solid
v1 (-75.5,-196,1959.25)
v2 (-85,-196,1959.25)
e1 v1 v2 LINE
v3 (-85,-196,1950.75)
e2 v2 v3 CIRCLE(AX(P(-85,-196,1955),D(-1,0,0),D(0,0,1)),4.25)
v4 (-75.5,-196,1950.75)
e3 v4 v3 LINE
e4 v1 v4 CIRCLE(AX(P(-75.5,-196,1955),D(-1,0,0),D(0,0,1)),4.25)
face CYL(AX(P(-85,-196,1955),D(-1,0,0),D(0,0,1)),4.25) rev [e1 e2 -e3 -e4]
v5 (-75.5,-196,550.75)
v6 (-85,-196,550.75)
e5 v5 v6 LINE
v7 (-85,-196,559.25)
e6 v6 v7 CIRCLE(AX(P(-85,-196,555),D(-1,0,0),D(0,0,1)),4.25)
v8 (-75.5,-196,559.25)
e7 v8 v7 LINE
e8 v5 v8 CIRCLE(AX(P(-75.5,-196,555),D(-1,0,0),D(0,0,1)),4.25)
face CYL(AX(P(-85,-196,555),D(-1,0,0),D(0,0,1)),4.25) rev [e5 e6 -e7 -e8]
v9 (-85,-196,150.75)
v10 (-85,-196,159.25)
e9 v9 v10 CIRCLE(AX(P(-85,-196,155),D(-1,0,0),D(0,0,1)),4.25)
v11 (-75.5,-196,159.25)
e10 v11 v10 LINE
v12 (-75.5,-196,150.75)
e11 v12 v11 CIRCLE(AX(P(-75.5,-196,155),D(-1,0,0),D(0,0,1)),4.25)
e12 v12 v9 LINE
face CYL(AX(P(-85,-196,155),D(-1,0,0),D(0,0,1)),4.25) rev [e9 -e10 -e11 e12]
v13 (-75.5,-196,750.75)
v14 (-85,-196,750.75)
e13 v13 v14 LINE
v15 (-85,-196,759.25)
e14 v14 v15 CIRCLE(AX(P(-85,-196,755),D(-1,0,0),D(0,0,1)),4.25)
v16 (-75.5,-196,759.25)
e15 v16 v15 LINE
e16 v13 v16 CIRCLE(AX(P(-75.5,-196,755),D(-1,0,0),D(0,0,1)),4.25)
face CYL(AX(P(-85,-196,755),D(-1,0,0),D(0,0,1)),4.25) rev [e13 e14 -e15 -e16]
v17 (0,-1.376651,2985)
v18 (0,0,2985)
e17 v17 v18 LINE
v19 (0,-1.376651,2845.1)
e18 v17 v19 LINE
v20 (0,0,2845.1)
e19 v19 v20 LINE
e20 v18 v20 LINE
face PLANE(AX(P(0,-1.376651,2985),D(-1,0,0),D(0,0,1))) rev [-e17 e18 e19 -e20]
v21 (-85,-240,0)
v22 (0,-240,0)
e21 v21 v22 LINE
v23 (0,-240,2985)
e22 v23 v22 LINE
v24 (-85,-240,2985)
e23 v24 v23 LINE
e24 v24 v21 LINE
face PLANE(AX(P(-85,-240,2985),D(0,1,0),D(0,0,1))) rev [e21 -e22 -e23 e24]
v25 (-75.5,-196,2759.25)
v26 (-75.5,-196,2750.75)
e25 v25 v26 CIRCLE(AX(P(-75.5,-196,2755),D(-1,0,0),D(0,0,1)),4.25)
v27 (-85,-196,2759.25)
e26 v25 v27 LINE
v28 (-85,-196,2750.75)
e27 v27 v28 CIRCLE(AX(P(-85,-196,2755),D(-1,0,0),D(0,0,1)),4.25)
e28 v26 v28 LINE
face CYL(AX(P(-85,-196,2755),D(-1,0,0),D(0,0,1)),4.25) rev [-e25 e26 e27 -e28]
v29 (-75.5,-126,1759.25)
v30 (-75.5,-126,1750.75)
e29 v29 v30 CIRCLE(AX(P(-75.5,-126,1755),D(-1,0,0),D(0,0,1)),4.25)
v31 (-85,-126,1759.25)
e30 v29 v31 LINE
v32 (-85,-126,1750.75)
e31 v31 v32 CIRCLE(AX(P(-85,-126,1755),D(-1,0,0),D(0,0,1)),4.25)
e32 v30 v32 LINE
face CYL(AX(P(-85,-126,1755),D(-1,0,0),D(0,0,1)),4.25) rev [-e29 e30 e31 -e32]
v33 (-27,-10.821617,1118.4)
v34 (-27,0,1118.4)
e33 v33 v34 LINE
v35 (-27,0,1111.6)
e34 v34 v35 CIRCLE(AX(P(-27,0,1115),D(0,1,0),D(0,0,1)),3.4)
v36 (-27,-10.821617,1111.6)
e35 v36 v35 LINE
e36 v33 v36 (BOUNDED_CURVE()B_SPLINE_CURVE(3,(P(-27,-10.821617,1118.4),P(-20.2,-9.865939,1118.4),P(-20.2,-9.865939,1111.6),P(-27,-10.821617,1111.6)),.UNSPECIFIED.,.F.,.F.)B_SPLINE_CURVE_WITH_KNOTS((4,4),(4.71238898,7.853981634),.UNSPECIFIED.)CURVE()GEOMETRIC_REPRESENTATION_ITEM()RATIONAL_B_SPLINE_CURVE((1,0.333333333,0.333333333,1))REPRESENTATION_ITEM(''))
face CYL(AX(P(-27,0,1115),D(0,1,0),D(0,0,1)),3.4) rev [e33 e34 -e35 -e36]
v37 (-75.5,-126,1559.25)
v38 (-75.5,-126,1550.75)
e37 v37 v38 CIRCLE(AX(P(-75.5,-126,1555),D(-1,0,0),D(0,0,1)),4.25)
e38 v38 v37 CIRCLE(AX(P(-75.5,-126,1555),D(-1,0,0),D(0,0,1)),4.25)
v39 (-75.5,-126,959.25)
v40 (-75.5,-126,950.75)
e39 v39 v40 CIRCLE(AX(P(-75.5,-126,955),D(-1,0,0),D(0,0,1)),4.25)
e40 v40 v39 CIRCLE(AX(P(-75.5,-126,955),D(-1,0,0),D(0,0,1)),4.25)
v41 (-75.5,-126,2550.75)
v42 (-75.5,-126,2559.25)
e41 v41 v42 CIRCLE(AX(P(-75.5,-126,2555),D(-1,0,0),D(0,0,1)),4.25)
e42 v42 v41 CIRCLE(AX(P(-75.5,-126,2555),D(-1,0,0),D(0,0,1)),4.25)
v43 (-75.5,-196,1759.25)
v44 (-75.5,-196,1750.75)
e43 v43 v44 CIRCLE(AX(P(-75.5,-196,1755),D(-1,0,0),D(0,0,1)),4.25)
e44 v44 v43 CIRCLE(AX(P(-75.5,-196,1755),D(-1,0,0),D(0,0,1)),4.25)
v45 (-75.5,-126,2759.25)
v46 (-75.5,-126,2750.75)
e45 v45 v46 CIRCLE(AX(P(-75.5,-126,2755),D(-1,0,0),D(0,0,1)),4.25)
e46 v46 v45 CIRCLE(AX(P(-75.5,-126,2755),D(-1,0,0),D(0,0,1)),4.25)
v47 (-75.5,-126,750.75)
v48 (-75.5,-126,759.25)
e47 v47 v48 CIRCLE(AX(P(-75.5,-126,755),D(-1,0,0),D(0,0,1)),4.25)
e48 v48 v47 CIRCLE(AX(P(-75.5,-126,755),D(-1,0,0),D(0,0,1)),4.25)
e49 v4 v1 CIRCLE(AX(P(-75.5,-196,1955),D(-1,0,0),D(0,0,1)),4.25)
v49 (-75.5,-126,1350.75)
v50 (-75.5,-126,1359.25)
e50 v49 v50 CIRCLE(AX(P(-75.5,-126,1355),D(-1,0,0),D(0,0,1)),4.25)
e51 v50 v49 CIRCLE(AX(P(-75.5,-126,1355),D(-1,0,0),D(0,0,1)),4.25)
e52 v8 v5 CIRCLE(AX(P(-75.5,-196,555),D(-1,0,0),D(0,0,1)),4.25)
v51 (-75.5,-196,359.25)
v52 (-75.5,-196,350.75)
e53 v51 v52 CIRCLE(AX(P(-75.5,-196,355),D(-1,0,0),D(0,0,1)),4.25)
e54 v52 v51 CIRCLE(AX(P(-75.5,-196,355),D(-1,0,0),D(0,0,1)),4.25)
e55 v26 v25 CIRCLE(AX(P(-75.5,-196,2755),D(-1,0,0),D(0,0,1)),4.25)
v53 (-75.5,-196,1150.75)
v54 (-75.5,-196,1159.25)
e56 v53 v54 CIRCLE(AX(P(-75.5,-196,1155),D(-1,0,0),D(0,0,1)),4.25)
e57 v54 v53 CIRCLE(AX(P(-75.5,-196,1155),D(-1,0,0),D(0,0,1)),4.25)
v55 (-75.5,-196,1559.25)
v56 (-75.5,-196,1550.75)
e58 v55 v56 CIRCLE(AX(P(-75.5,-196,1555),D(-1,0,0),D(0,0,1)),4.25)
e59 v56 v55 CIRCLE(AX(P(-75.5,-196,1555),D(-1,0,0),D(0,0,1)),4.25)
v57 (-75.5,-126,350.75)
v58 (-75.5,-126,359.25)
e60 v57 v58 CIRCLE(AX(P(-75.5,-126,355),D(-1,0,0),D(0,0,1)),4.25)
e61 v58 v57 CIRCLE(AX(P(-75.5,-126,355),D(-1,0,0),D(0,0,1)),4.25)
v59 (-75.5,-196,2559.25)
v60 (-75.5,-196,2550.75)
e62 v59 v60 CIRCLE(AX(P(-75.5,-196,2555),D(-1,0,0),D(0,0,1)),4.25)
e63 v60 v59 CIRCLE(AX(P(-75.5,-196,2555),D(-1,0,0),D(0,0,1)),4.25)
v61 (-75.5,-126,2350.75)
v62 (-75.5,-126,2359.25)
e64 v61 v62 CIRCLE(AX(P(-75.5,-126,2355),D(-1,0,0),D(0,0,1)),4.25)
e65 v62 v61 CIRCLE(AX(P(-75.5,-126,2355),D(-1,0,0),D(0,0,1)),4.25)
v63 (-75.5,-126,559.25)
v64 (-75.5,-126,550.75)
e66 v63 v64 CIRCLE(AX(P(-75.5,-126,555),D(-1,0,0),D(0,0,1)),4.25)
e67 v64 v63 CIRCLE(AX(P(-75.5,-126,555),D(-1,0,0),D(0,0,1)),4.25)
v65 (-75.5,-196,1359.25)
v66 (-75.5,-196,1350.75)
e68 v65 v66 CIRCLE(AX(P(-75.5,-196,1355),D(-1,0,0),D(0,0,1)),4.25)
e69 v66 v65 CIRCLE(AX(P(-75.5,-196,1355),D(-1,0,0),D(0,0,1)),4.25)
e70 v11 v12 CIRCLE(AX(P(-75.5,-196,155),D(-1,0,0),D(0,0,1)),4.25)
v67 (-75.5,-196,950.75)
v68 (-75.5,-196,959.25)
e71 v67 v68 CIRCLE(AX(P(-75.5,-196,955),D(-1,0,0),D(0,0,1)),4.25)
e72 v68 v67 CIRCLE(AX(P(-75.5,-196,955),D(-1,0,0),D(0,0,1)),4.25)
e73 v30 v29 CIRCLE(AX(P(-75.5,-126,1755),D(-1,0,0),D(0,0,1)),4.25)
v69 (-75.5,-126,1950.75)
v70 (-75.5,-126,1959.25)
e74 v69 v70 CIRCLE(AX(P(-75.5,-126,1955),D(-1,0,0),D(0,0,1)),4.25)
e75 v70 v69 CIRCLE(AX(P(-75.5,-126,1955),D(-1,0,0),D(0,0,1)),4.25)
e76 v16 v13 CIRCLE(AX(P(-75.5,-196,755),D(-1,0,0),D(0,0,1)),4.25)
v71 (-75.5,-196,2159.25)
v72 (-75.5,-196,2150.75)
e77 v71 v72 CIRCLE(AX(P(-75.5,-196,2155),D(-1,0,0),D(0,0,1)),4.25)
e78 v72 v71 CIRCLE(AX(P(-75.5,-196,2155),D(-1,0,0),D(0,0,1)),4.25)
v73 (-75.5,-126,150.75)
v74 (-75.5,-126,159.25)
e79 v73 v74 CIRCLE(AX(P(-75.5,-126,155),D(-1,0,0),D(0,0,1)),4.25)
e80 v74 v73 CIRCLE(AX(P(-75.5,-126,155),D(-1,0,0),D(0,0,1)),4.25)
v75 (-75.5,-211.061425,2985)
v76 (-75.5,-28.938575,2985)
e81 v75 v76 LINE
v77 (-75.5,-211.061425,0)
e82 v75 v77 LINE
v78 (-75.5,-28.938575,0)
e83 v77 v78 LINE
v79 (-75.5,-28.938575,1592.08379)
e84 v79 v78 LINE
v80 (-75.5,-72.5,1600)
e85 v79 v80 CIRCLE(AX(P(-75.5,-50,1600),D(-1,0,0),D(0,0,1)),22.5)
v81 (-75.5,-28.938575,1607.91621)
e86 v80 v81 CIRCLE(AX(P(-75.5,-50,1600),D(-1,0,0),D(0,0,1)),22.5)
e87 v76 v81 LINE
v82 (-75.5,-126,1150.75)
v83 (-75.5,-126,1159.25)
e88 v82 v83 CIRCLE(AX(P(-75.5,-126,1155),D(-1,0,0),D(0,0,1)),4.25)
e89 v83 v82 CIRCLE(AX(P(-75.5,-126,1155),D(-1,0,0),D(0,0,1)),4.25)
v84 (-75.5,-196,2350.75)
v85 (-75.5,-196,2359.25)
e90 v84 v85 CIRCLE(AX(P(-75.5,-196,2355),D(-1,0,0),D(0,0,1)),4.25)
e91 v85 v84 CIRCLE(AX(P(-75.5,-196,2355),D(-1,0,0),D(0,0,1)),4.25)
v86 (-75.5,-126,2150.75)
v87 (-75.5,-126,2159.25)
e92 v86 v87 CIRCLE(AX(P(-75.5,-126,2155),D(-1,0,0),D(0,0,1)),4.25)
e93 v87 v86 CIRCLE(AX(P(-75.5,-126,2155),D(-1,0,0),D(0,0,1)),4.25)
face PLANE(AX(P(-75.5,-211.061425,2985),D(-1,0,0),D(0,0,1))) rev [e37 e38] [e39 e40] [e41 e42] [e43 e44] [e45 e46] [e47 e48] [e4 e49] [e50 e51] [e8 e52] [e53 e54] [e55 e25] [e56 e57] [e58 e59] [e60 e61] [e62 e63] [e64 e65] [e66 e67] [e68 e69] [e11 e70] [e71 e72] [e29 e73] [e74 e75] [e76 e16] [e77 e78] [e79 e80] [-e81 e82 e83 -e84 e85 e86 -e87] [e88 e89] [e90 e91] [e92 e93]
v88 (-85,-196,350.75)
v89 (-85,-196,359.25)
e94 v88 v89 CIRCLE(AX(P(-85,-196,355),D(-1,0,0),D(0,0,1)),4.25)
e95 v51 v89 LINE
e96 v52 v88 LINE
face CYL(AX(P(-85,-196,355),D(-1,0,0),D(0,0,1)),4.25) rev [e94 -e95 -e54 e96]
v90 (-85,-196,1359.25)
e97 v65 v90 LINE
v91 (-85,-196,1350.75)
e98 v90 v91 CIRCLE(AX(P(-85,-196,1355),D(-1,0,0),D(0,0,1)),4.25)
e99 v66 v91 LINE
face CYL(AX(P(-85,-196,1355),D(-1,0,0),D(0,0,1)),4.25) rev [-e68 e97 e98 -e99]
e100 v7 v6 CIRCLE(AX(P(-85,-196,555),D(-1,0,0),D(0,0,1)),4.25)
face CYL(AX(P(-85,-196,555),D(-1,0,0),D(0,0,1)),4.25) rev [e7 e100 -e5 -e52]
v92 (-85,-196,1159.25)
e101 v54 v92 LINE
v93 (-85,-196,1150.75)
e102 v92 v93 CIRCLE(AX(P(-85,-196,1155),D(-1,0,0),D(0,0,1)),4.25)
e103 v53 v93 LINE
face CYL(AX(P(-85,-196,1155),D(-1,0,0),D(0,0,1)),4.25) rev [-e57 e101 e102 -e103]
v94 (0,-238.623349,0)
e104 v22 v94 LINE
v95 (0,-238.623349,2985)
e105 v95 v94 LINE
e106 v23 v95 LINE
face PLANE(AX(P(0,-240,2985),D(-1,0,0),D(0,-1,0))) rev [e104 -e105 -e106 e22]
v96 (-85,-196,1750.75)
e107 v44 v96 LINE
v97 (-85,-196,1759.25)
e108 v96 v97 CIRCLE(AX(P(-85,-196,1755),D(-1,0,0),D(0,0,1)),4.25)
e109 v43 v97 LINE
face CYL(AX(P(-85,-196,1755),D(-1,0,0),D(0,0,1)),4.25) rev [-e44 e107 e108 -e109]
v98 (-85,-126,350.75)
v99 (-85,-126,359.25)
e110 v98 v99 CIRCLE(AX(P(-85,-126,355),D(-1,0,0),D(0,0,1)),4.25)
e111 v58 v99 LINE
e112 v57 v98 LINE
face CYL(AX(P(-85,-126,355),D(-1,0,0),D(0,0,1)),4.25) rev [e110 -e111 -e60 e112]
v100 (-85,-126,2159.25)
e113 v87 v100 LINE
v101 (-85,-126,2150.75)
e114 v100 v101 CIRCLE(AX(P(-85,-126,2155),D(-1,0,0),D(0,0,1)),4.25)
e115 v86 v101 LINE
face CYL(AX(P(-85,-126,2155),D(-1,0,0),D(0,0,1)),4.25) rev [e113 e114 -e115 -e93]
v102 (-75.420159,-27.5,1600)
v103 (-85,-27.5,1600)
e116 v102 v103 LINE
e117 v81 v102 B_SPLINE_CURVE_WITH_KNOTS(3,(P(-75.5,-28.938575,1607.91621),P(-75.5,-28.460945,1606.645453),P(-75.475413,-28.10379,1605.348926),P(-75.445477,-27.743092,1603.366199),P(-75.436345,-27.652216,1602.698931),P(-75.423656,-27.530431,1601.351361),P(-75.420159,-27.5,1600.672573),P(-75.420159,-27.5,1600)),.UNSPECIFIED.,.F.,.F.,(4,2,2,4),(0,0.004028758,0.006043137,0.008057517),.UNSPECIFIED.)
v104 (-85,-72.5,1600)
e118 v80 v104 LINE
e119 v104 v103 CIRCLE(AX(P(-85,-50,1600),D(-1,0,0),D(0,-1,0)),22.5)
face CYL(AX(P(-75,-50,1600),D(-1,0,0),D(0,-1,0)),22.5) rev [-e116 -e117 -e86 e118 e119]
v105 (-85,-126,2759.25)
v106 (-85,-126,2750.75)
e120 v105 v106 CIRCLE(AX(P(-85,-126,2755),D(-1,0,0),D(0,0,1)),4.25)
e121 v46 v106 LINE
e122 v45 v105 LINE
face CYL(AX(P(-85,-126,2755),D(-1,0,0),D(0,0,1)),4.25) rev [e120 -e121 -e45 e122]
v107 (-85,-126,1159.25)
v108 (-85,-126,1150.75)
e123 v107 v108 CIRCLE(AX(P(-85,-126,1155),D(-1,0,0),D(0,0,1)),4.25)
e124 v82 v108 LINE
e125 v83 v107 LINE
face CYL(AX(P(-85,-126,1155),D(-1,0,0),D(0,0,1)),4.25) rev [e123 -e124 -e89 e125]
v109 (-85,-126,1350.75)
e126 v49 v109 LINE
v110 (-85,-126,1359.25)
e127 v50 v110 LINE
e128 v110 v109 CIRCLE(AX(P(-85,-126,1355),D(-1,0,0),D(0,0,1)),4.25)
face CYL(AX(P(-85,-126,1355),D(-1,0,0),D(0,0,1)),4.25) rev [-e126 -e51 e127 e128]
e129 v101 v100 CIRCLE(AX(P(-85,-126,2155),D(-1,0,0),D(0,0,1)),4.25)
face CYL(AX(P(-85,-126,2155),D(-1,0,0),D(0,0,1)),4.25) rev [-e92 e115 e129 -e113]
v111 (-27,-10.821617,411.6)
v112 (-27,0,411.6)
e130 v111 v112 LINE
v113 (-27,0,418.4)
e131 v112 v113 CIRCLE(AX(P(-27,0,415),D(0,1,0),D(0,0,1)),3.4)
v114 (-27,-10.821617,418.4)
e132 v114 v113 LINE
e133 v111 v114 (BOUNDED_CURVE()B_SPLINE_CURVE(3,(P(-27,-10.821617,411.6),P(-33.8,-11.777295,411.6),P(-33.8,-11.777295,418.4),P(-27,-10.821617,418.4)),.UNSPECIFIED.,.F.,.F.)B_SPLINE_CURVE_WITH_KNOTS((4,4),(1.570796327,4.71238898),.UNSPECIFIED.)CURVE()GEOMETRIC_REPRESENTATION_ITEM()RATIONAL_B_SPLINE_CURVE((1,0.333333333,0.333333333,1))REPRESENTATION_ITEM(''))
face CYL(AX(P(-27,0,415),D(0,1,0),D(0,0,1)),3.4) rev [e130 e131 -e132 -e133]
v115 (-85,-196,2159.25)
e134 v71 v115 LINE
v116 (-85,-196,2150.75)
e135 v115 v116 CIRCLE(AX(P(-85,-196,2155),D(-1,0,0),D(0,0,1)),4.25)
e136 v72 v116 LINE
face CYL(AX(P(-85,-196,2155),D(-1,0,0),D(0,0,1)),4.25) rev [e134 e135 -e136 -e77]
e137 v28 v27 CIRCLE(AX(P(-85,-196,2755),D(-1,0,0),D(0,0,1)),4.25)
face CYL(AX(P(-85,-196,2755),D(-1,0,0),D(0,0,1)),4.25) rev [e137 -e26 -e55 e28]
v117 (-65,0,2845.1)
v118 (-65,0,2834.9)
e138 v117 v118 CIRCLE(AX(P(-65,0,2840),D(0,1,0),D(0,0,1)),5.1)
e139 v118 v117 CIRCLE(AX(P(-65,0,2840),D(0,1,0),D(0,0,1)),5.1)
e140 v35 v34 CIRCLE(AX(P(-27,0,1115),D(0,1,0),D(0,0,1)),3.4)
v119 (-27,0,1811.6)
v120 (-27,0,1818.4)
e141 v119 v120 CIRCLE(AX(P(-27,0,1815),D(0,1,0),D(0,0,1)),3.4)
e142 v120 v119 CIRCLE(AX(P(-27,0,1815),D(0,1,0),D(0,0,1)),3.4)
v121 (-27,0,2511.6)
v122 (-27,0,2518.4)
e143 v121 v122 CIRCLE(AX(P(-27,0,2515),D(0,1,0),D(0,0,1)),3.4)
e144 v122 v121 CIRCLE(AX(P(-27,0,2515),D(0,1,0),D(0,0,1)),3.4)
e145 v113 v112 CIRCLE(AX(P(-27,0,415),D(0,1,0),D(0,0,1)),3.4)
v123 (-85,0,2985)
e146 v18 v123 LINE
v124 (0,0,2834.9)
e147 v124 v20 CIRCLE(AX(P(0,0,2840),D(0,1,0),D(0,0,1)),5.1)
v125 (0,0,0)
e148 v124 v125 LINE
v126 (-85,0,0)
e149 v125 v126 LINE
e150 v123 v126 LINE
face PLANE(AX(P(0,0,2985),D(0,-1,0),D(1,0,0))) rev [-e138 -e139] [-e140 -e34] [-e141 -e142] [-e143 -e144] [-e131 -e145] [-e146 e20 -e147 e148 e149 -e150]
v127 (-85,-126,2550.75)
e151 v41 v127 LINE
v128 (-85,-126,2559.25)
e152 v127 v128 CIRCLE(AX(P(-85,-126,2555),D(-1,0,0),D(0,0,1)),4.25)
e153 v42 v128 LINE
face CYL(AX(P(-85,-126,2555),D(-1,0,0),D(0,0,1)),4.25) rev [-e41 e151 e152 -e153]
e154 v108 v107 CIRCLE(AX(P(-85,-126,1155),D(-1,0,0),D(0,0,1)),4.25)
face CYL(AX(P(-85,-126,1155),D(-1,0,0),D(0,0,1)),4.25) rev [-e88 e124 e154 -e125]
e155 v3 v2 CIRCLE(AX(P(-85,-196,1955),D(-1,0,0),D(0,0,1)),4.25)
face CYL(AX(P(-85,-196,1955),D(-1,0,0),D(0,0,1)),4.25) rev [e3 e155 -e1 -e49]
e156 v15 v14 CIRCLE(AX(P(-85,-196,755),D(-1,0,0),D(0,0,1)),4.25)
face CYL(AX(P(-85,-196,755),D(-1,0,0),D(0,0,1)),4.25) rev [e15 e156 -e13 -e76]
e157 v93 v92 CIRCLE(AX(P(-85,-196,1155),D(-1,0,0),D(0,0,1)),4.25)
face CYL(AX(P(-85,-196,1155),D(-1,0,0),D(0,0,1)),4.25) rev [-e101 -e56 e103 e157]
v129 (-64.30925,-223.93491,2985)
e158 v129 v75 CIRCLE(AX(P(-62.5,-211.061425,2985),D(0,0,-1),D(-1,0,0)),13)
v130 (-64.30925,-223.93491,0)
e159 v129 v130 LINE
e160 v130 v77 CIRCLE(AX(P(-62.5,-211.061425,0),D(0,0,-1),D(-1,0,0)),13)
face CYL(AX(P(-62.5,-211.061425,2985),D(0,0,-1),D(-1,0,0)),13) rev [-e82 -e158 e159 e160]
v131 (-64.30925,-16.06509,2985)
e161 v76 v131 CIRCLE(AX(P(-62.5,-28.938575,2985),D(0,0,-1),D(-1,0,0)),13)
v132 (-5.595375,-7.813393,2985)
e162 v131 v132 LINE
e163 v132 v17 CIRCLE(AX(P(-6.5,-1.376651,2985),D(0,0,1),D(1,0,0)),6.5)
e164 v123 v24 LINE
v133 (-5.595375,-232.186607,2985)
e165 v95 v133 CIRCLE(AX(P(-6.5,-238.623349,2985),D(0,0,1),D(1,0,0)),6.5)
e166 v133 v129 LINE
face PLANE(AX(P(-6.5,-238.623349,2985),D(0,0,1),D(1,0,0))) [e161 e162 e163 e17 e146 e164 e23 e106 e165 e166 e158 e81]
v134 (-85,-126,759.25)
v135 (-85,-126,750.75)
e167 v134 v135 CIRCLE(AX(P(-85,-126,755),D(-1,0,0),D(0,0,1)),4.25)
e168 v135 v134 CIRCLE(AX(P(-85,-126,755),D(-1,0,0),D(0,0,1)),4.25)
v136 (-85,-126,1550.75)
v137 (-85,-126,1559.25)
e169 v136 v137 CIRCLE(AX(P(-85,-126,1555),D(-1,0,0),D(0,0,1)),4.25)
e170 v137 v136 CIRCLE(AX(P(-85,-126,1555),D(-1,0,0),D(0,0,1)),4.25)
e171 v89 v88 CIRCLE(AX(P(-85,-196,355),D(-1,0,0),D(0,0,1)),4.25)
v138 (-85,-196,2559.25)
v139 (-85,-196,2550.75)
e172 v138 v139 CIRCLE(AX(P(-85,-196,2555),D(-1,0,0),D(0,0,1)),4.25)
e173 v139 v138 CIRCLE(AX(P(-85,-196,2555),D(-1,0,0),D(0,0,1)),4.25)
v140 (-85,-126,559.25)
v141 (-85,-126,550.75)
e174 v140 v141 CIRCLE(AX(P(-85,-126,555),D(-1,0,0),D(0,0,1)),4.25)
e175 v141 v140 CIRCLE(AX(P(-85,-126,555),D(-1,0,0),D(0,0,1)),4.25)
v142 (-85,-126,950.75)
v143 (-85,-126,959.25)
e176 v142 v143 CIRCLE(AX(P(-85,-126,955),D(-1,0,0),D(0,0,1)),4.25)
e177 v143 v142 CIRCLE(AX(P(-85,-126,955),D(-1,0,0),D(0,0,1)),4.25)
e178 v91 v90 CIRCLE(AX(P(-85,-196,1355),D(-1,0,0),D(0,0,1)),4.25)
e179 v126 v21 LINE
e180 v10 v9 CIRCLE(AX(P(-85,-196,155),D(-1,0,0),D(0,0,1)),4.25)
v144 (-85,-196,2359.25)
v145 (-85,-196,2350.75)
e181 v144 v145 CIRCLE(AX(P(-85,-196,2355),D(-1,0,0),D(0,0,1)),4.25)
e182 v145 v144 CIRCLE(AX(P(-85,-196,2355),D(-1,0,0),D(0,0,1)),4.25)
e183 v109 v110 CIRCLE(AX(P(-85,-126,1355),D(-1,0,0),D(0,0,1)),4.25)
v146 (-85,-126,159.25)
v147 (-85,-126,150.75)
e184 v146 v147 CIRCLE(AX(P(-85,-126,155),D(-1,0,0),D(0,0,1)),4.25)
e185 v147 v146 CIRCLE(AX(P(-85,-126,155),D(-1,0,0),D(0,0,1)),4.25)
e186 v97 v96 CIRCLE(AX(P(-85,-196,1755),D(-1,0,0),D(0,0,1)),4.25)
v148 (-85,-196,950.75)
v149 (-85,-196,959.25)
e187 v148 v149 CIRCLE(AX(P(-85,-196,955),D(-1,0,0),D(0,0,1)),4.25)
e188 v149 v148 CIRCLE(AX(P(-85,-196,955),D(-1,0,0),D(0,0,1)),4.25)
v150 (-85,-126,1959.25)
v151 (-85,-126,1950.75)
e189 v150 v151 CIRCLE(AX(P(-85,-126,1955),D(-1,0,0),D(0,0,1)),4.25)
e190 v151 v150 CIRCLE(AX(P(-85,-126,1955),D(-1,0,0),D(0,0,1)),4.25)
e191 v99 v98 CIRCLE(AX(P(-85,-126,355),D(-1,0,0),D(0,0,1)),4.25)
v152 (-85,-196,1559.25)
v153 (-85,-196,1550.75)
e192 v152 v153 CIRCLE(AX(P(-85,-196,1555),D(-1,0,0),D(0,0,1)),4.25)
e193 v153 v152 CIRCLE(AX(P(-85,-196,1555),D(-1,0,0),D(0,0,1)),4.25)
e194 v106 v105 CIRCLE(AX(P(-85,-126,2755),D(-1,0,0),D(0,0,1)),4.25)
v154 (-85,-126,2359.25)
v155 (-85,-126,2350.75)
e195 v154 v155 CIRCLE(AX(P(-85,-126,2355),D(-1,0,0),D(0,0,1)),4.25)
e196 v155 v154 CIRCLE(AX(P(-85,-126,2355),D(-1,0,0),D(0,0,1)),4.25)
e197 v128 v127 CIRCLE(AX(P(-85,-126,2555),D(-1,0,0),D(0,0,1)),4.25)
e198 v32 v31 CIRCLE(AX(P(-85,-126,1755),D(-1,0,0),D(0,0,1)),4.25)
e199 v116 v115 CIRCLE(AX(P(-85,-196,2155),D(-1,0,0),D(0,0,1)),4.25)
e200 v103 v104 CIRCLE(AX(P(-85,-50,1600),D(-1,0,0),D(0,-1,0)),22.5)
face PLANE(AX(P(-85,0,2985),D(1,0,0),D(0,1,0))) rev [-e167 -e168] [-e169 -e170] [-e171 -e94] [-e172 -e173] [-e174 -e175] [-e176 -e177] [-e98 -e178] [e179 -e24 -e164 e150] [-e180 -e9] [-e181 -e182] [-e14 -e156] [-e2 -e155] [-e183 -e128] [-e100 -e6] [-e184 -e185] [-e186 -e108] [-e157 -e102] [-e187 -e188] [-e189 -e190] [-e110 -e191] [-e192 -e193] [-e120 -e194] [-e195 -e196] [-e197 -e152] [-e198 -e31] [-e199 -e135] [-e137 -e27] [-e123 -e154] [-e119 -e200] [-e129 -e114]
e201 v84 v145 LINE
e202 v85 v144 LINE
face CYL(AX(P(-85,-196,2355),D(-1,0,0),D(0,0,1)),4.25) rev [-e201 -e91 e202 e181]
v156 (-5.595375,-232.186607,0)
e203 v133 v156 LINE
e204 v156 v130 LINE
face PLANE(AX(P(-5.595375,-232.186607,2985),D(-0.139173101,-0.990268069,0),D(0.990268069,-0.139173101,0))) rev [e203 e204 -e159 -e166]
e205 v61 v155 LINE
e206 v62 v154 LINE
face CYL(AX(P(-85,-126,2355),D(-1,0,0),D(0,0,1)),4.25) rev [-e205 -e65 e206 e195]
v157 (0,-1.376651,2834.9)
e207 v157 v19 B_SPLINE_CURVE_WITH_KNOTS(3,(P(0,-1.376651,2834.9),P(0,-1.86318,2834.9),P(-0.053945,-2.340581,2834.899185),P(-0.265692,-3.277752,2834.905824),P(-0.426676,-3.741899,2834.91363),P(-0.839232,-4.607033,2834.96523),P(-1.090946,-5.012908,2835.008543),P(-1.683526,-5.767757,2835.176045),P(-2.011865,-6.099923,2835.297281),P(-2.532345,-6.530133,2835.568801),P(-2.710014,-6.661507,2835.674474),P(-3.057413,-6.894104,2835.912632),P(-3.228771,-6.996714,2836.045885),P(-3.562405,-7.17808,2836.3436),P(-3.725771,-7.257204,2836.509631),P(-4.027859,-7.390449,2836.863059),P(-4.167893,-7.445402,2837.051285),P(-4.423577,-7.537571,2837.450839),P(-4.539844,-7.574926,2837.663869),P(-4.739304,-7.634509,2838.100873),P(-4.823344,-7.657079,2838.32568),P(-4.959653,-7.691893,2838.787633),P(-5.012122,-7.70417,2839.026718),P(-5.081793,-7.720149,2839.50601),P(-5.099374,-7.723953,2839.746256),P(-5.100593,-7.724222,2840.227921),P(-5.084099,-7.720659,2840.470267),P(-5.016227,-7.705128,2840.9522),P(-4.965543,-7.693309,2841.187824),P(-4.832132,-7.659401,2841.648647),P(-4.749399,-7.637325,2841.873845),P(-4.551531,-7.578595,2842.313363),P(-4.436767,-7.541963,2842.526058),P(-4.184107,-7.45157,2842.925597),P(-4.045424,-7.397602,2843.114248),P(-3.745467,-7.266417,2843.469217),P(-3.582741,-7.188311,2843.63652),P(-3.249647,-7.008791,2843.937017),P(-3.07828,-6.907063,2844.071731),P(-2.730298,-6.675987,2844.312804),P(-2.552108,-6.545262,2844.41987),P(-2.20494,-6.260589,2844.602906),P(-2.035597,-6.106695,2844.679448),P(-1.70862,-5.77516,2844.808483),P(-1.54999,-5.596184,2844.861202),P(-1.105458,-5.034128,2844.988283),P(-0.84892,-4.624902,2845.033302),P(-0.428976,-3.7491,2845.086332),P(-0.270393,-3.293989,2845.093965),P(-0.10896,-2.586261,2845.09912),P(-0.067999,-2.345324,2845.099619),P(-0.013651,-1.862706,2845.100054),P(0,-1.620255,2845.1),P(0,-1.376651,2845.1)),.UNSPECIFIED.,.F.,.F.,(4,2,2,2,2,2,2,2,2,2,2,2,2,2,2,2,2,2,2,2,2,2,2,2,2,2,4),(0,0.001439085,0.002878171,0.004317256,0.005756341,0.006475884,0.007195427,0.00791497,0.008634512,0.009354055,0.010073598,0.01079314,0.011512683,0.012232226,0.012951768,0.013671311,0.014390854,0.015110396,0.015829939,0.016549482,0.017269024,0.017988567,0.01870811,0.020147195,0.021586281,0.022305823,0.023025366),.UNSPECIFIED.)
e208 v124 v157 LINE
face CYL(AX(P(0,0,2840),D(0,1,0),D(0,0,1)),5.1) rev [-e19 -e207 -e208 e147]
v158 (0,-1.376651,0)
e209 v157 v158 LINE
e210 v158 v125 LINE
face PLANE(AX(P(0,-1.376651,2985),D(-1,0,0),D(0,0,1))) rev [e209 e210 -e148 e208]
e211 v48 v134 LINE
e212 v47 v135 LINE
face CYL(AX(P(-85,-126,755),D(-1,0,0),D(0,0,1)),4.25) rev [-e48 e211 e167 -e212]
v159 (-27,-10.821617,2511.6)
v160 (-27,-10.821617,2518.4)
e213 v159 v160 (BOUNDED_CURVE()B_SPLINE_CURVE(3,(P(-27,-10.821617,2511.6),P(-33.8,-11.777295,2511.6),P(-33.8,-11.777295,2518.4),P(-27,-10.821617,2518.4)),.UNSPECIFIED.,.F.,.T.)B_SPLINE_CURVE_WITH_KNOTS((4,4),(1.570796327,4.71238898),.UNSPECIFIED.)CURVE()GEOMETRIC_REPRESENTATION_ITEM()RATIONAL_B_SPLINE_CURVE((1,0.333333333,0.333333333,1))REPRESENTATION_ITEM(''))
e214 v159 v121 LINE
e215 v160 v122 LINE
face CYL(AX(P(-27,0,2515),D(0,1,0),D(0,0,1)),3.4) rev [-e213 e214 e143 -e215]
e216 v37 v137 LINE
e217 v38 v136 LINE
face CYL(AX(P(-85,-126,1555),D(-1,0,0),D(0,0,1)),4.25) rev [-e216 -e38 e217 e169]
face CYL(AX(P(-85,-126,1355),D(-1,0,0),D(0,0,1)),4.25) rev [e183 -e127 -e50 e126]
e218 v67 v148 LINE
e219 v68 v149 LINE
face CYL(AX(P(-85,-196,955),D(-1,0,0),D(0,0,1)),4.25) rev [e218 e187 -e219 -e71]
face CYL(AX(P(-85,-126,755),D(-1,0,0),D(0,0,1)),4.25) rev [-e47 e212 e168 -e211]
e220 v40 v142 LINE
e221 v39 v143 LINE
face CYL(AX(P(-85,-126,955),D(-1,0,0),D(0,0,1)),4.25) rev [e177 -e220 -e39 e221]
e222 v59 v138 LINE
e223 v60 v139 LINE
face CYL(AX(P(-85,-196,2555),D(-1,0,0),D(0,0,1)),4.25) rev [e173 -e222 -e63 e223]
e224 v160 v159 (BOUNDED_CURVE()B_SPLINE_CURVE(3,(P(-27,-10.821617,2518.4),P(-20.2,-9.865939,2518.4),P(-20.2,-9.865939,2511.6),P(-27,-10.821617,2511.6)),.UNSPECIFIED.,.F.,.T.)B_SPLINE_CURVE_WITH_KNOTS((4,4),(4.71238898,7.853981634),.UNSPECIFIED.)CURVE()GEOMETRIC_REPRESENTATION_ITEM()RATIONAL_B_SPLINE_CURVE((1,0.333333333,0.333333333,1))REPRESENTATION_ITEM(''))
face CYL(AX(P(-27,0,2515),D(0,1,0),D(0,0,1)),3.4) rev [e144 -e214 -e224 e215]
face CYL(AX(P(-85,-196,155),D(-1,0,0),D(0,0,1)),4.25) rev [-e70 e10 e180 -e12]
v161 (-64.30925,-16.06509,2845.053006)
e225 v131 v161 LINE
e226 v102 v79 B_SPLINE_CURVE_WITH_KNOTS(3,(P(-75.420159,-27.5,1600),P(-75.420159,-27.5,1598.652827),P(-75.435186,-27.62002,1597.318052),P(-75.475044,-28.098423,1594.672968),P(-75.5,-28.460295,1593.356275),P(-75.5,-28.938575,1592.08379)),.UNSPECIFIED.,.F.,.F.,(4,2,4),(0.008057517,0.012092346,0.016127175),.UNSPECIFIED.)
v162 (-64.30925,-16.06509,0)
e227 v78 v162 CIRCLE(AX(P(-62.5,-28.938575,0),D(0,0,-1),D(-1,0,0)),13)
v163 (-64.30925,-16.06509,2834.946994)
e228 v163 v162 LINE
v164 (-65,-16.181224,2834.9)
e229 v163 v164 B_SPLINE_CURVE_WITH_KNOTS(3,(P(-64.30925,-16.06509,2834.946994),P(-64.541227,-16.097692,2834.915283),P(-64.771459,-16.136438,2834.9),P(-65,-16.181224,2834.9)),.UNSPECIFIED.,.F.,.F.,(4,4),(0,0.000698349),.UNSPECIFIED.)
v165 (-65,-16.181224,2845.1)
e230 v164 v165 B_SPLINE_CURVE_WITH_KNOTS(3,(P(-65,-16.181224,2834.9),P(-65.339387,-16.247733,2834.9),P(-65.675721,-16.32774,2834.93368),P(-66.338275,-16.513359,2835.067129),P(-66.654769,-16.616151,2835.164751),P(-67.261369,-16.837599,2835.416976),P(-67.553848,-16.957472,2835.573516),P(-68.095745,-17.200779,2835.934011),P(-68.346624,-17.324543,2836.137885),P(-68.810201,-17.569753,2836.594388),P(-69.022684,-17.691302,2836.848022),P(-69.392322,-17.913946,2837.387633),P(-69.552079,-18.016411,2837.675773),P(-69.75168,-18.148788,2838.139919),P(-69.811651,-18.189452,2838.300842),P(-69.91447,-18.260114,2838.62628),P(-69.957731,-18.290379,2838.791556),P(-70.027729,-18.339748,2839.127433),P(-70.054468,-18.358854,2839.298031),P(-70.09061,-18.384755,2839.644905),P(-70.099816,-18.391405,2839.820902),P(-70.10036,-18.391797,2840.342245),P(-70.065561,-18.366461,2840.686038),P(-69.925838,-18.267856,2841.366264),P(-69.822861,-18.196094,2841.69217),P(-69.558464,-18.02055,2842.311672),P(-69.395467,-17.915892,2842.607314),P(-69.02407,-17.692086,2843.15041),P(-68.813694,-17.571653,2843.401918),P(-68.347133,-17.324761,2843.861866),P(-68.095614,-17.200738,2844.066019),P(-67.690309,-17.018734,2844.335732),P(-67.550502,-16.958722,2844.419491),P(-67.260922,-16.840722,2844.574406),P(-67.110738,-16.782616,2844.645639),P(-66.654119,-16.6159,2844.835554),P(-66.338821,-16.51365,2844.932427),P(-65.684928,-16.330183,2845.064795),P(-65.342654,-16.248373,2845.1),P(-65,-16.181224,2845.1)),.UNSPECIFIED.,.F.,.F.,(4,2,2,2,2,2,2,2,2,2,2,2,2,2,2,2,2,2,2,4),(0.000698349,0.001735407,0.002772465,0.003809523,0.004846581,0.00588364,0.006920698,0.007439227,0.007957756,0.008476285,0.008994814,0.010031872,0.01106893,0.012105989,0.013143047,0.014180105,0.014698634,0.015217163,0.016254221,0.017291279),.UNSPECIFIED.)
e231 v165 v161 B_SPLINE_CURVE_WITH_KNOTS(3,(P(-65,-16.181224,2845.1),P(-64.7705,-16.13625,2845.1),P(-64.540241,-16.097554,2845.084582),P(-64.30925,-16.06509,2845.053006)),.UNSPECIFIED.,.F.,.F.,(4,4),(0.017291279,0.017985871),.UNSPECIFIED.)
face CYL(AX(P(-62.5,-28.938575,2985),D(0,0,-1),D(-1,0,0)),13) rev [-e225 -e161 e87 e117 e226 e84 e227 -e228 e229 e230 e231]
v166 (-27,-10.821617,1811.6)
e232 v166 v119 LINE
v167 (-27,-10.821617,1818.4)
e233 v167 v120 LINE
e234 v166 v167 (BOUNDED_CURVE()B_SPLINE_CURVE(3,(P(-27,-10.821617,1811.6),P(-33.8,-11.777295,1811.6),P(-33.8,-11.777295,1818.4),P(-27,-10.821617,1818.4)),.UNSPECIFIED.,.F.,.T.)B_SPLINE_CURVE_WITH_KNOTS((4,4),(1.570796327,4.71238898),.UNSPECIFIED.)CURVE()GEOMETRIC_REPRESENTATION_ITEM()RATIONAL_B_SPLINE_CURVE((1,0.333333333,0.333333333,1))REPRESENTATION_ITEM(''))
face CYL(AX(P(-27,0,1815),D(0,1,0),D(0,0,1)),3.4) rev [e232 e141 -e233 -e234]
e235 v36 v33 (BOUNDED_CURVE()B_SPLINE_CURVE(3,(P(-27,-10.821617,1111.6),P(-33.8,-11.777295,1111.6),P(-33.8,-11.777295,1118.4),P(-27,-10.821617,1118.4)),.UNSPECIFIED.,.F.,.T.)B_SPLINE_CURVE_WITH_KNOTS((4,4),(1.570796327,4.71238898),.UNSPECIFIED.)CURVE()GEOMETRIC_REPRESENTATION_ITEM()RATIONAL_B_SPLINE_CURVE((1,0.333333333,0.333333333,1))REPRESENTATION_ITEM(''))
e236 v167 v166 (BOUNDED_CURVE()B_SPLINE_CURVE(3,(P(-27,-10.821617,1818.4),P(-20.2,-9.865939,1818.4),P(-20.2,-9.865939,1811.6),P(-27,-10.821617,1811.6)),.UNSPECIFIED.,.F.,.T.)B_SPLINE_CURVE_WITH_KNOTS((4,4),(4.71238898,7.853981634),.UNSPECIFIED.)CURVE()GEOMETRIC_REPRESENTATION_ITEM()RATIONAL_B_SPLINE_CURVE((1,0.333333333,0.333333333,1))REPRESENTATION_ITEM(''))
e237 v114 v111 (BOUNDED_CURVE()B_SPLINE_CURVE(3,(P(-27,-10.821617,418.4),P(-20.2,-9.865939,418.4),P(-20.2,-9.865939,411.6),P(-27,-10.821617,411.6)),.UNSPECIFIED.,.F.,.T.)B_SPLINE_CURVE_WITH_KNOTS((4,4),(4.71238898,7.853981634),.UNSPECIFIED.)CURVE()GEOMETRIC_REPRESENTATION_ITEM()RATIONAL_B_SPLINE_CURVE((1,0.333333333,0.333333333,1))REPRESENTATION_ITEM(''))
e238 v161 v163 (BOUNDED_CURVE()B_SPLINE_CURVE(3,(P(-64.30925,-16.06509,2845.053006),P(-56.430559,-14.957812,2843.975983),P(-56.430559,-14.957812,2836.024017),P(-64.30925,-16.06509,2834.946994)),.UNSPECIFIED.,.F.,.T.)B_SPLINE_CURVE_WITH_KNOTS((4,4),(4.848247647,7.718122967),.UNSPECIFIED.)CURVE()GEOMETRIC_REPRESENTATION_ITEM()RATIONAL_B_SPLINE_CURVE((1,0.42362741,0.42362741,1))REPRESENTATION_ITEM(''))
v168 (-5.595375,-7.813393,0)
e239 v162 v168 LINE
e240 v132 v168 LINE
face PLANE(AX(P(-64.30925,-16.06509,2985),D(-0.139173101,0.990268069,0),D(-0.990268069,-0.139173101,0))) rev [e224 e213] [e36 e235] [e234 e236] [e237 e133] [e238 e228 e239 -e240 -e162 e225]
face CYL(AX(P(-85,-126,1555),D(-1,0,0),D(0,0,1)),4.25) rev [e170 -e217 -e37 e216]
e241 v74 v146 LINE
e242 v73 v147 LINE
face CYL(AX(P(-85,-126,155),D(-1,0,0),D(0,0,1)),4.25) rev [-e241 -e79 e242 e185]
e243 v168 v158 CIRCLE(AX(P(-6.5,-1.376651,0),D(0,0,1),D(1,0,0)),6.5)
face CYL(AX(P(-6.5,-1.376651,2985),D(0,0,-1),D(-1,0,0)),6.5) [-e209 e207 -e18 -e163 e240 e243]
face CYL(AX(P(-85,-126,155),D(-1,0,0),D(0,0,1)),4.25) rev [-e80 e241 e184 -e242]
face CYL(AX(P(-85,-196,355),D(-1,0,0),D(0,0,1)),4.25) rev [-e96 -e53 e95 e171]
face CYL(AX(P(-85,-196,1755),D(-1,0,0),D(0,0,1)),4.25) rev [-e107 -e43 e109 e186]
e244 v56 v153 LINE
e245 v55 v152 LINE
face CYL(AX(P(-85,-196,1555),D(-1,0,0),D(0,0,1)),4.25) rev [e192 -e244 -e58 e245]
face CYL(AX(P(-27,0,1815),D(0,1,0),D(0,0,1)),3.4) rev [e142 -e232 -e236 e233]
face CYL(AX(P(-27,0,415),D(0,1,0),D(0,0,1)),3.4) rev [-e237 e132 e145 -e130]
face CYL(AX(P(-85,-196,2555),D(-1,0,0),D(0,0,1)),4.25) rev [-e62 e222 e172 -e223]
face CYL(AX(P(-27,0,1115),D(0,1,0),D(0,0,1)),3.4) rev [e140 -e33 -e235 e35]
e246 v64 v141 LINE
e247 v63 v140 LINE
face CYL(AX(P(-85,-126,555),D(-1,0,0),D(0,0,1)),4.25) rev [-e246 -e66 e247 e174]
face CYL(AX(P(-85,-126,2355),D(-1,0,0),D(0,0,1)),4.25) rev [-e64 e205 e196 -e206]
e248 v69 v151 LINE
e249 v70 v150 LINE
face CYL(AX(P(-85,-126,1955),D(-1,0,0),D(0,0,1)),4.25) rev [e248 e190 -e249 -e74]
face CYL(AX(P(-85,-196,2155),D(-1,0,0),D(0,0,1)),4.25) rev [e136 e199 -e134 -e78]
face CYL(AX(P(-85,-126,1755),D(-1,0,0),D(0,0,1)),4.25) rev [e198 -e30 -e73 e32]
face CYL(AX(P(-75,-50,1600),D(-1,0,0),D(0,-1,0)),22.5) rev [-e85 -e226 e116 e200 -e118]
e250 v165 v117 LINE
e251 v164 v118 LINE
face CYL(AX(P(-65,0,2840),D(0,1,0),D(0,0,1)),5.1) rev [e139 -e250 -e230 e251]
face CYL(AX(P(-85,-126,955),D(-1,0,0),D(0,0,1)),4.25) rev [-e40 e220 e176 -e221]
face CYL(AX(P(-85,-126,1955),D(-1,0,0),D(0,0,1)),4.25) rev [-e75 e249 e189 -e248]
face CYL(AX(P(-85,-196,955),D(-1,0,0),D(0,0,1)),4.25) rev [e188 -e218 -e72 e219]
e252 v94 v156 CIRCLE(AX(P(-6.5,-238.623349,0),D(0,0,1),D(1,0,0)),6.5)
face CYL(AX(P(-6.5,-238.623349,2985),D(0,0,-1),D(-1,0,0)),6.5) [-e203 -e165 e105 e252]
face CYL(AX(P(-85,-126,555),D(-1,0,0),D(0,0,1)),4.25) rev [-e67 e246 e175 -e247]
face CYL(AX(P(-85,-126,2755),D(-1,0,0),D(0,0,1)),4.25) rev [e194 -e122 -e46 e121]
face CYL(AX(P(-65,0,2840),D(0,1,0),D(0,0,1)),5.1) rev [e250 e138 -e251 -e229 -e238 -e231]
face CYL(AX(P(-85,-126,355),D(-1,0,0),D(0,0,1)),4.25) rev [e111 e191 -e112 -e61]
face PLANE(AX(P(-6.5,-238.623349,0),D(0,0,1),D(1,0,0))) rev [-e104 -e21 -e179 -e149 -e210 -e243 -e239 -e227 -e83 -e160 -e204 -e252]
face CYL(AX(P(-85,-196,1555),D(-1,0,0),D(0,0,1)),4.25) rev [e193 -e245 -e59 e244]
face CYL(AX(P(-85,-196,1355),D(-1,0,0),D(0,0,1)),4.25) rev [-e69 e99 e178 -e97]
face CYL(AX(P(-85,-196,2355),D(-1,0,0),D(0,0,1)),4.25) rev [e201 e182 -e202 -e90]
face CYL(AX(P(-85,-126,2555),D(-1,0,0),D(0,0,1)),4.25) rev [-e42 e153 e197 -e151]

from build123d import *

# Parameters (mm, degrees)
EXTRUDE_1_DEPTH         = 2985
HOLE_WIZARD_M10_2_D     = 8.5
HOLE_WIZARD_M10_2_DEPTH = 24.5
HOLE_WIZARD_M10_2_TIP   = 2.553657631
HOLE_WIZARD_M8_1_D      = 6.8
HOLE_WIZARD_M8_1_DEPTH  = 19.75
HOLE_WIZARD_M8_1_TIP    = 2.042926105
HOLE_WIZARD_M12_1_D     = 10.2
HOLE_WIZARD_M12_1_DEPTH = 29.25
HOLE_WIZARD_M12_1_TIP   = 3.064389157
SKETCH_14_R             = 22.5
CUT_EXTRUDE_1_DEPTH     = 10


with BuildPart() as part:
    # 草图1 → 凸台-拉伸1 (new body)
    with BuildSketch(Plane.XY):
        with BuildLine():
            Line((0, 0), (-85, 0))
            Line((-85, 0), (-85, -240))
            Line((-85, -240), (0, -240))
            Line((0, -240), (0, -238.623349271))
            ThreePointArc((0, -238.623349271), (-1.594387729, -234.358965582), (-5.595374844, -232.186606824))
            Line((-5.595374844, -232.186606824), (-64.309250312, -223.934909757))
            ThreePointArc((-64.309250312, -223.934909757), (-72.311224543, -219.59019224), (-75.5, -211.061424863))
            Line((-75.5, -211.061424863), (-75.5, -28.938575137))
            ThreePointArc((-75.5, -28.938575137), (-72.311224543, -20.40980776), (-64.309250312, -16.065090243))
            Line((-64.309250312, -16.065090243), (-5.595374844, -7.813393176))
            ThreePointArc((-5.595374844, -7.813393176), (-1.594387729, -5.641034418), (0, -1.376650729))
            Line((0, -1.376650729), (0, 0))
        make_face()
    extrude(amount=EXTRUDE_1_DEPTH)

    # M10 螺纹孔2
    with Locations(Plane.ZY.offset(85)):
        with Locations((155, -126), (155, -196), (355, -126), (355, -196), (555, -126), (555, -196), (755, -126), (755, -196), (955, -126), (955, -196), (1155, -126), (1155, -196), (1355, -126), (1355, -196), (1555, -196), (1555, -126), (1755, -196), (1755, -126), (1955, -126), (1955, -196), (2155, -196), (2155, -126), (2355, -126), (2355, -196), (2555, -196), (2555, -126), (2755, -126), (2755, -196)):
            Hole(HOLE_WIZARD_M10_2_D / 2, depth=HOLE_WIZARD_M10_2_DEPTH)
            with Locations((0, 0, -(HOLE_WIZARD_M10_2_DEPTH + HOLE_WIZARD_M10_2_TIP / 2))):  # 118° drill point
                Cone(0, HOLE_WIZARD_M10_2_D / 2, HOLE_WIZARD_M10_2_TIP, mode=Mode.SUBTRACT)

    # M8 螺纹孔1
    with Locations(Plane(origin=(0, 0, 0), x_dir=(1, 0, 0), z_dir=(0, 1, 0))):
        with Locations((-27, -415), (-27, -1115), (-27, -1815), (-27, -2515)):
            Hole(HOLE_WIZARD_M8_1_D / 2, depth=HOLE_WIZARD_M8_1_DEPTH)
            with Locations((0, 0, -(HOLE_WIZARD_M8_1_DEPTH + HOLE_WIZARD_M8_1_TIP / 2))):  # 118° drill point
                Cone(0, HOLE_WIZARD_M8_1_D / 2, HOLE_WIZARD_M8_1_TIP, mode=Mode.SUBTRACT)

    # M12 螺纹孔1
    with Locations(Plane(origin=(0, 0, 0), x_dir=(1, 0, 0), z_dir=(0, 1, 0))):
        with Locations((-65, -2840), (0, -2840)):
            Hole(HOLE_WIZARD_M12_1_D / 2, depth=HOLE_WIZARD_M12_1_DEPTH)
            with Locations((0, 0, -(HOLE_WIZARD_M12_1_DEPTH + HOLE_WIZARD_M12_1_TIP / 2))):  # 118° drill point
                Cone(0, HOLE_WIZARD_M12_1_D / 2, HOLE_WIZARD_M12_1_TIP, mode=Mode.SUBTRACT)

    # 草图14 → 切除-拉伸1 (cut)
    with BuildSketch(Plane.ZY.offset(85)):
        with Locations(Location((1600, -50, 0), (0, 0, 270))):
            Circle(SKETCH_14_R)
    extrude(amount=-CUT_EXTRUDE_1_DEPTH, mode=Mode.SUBTRACT)


solid = part.part
